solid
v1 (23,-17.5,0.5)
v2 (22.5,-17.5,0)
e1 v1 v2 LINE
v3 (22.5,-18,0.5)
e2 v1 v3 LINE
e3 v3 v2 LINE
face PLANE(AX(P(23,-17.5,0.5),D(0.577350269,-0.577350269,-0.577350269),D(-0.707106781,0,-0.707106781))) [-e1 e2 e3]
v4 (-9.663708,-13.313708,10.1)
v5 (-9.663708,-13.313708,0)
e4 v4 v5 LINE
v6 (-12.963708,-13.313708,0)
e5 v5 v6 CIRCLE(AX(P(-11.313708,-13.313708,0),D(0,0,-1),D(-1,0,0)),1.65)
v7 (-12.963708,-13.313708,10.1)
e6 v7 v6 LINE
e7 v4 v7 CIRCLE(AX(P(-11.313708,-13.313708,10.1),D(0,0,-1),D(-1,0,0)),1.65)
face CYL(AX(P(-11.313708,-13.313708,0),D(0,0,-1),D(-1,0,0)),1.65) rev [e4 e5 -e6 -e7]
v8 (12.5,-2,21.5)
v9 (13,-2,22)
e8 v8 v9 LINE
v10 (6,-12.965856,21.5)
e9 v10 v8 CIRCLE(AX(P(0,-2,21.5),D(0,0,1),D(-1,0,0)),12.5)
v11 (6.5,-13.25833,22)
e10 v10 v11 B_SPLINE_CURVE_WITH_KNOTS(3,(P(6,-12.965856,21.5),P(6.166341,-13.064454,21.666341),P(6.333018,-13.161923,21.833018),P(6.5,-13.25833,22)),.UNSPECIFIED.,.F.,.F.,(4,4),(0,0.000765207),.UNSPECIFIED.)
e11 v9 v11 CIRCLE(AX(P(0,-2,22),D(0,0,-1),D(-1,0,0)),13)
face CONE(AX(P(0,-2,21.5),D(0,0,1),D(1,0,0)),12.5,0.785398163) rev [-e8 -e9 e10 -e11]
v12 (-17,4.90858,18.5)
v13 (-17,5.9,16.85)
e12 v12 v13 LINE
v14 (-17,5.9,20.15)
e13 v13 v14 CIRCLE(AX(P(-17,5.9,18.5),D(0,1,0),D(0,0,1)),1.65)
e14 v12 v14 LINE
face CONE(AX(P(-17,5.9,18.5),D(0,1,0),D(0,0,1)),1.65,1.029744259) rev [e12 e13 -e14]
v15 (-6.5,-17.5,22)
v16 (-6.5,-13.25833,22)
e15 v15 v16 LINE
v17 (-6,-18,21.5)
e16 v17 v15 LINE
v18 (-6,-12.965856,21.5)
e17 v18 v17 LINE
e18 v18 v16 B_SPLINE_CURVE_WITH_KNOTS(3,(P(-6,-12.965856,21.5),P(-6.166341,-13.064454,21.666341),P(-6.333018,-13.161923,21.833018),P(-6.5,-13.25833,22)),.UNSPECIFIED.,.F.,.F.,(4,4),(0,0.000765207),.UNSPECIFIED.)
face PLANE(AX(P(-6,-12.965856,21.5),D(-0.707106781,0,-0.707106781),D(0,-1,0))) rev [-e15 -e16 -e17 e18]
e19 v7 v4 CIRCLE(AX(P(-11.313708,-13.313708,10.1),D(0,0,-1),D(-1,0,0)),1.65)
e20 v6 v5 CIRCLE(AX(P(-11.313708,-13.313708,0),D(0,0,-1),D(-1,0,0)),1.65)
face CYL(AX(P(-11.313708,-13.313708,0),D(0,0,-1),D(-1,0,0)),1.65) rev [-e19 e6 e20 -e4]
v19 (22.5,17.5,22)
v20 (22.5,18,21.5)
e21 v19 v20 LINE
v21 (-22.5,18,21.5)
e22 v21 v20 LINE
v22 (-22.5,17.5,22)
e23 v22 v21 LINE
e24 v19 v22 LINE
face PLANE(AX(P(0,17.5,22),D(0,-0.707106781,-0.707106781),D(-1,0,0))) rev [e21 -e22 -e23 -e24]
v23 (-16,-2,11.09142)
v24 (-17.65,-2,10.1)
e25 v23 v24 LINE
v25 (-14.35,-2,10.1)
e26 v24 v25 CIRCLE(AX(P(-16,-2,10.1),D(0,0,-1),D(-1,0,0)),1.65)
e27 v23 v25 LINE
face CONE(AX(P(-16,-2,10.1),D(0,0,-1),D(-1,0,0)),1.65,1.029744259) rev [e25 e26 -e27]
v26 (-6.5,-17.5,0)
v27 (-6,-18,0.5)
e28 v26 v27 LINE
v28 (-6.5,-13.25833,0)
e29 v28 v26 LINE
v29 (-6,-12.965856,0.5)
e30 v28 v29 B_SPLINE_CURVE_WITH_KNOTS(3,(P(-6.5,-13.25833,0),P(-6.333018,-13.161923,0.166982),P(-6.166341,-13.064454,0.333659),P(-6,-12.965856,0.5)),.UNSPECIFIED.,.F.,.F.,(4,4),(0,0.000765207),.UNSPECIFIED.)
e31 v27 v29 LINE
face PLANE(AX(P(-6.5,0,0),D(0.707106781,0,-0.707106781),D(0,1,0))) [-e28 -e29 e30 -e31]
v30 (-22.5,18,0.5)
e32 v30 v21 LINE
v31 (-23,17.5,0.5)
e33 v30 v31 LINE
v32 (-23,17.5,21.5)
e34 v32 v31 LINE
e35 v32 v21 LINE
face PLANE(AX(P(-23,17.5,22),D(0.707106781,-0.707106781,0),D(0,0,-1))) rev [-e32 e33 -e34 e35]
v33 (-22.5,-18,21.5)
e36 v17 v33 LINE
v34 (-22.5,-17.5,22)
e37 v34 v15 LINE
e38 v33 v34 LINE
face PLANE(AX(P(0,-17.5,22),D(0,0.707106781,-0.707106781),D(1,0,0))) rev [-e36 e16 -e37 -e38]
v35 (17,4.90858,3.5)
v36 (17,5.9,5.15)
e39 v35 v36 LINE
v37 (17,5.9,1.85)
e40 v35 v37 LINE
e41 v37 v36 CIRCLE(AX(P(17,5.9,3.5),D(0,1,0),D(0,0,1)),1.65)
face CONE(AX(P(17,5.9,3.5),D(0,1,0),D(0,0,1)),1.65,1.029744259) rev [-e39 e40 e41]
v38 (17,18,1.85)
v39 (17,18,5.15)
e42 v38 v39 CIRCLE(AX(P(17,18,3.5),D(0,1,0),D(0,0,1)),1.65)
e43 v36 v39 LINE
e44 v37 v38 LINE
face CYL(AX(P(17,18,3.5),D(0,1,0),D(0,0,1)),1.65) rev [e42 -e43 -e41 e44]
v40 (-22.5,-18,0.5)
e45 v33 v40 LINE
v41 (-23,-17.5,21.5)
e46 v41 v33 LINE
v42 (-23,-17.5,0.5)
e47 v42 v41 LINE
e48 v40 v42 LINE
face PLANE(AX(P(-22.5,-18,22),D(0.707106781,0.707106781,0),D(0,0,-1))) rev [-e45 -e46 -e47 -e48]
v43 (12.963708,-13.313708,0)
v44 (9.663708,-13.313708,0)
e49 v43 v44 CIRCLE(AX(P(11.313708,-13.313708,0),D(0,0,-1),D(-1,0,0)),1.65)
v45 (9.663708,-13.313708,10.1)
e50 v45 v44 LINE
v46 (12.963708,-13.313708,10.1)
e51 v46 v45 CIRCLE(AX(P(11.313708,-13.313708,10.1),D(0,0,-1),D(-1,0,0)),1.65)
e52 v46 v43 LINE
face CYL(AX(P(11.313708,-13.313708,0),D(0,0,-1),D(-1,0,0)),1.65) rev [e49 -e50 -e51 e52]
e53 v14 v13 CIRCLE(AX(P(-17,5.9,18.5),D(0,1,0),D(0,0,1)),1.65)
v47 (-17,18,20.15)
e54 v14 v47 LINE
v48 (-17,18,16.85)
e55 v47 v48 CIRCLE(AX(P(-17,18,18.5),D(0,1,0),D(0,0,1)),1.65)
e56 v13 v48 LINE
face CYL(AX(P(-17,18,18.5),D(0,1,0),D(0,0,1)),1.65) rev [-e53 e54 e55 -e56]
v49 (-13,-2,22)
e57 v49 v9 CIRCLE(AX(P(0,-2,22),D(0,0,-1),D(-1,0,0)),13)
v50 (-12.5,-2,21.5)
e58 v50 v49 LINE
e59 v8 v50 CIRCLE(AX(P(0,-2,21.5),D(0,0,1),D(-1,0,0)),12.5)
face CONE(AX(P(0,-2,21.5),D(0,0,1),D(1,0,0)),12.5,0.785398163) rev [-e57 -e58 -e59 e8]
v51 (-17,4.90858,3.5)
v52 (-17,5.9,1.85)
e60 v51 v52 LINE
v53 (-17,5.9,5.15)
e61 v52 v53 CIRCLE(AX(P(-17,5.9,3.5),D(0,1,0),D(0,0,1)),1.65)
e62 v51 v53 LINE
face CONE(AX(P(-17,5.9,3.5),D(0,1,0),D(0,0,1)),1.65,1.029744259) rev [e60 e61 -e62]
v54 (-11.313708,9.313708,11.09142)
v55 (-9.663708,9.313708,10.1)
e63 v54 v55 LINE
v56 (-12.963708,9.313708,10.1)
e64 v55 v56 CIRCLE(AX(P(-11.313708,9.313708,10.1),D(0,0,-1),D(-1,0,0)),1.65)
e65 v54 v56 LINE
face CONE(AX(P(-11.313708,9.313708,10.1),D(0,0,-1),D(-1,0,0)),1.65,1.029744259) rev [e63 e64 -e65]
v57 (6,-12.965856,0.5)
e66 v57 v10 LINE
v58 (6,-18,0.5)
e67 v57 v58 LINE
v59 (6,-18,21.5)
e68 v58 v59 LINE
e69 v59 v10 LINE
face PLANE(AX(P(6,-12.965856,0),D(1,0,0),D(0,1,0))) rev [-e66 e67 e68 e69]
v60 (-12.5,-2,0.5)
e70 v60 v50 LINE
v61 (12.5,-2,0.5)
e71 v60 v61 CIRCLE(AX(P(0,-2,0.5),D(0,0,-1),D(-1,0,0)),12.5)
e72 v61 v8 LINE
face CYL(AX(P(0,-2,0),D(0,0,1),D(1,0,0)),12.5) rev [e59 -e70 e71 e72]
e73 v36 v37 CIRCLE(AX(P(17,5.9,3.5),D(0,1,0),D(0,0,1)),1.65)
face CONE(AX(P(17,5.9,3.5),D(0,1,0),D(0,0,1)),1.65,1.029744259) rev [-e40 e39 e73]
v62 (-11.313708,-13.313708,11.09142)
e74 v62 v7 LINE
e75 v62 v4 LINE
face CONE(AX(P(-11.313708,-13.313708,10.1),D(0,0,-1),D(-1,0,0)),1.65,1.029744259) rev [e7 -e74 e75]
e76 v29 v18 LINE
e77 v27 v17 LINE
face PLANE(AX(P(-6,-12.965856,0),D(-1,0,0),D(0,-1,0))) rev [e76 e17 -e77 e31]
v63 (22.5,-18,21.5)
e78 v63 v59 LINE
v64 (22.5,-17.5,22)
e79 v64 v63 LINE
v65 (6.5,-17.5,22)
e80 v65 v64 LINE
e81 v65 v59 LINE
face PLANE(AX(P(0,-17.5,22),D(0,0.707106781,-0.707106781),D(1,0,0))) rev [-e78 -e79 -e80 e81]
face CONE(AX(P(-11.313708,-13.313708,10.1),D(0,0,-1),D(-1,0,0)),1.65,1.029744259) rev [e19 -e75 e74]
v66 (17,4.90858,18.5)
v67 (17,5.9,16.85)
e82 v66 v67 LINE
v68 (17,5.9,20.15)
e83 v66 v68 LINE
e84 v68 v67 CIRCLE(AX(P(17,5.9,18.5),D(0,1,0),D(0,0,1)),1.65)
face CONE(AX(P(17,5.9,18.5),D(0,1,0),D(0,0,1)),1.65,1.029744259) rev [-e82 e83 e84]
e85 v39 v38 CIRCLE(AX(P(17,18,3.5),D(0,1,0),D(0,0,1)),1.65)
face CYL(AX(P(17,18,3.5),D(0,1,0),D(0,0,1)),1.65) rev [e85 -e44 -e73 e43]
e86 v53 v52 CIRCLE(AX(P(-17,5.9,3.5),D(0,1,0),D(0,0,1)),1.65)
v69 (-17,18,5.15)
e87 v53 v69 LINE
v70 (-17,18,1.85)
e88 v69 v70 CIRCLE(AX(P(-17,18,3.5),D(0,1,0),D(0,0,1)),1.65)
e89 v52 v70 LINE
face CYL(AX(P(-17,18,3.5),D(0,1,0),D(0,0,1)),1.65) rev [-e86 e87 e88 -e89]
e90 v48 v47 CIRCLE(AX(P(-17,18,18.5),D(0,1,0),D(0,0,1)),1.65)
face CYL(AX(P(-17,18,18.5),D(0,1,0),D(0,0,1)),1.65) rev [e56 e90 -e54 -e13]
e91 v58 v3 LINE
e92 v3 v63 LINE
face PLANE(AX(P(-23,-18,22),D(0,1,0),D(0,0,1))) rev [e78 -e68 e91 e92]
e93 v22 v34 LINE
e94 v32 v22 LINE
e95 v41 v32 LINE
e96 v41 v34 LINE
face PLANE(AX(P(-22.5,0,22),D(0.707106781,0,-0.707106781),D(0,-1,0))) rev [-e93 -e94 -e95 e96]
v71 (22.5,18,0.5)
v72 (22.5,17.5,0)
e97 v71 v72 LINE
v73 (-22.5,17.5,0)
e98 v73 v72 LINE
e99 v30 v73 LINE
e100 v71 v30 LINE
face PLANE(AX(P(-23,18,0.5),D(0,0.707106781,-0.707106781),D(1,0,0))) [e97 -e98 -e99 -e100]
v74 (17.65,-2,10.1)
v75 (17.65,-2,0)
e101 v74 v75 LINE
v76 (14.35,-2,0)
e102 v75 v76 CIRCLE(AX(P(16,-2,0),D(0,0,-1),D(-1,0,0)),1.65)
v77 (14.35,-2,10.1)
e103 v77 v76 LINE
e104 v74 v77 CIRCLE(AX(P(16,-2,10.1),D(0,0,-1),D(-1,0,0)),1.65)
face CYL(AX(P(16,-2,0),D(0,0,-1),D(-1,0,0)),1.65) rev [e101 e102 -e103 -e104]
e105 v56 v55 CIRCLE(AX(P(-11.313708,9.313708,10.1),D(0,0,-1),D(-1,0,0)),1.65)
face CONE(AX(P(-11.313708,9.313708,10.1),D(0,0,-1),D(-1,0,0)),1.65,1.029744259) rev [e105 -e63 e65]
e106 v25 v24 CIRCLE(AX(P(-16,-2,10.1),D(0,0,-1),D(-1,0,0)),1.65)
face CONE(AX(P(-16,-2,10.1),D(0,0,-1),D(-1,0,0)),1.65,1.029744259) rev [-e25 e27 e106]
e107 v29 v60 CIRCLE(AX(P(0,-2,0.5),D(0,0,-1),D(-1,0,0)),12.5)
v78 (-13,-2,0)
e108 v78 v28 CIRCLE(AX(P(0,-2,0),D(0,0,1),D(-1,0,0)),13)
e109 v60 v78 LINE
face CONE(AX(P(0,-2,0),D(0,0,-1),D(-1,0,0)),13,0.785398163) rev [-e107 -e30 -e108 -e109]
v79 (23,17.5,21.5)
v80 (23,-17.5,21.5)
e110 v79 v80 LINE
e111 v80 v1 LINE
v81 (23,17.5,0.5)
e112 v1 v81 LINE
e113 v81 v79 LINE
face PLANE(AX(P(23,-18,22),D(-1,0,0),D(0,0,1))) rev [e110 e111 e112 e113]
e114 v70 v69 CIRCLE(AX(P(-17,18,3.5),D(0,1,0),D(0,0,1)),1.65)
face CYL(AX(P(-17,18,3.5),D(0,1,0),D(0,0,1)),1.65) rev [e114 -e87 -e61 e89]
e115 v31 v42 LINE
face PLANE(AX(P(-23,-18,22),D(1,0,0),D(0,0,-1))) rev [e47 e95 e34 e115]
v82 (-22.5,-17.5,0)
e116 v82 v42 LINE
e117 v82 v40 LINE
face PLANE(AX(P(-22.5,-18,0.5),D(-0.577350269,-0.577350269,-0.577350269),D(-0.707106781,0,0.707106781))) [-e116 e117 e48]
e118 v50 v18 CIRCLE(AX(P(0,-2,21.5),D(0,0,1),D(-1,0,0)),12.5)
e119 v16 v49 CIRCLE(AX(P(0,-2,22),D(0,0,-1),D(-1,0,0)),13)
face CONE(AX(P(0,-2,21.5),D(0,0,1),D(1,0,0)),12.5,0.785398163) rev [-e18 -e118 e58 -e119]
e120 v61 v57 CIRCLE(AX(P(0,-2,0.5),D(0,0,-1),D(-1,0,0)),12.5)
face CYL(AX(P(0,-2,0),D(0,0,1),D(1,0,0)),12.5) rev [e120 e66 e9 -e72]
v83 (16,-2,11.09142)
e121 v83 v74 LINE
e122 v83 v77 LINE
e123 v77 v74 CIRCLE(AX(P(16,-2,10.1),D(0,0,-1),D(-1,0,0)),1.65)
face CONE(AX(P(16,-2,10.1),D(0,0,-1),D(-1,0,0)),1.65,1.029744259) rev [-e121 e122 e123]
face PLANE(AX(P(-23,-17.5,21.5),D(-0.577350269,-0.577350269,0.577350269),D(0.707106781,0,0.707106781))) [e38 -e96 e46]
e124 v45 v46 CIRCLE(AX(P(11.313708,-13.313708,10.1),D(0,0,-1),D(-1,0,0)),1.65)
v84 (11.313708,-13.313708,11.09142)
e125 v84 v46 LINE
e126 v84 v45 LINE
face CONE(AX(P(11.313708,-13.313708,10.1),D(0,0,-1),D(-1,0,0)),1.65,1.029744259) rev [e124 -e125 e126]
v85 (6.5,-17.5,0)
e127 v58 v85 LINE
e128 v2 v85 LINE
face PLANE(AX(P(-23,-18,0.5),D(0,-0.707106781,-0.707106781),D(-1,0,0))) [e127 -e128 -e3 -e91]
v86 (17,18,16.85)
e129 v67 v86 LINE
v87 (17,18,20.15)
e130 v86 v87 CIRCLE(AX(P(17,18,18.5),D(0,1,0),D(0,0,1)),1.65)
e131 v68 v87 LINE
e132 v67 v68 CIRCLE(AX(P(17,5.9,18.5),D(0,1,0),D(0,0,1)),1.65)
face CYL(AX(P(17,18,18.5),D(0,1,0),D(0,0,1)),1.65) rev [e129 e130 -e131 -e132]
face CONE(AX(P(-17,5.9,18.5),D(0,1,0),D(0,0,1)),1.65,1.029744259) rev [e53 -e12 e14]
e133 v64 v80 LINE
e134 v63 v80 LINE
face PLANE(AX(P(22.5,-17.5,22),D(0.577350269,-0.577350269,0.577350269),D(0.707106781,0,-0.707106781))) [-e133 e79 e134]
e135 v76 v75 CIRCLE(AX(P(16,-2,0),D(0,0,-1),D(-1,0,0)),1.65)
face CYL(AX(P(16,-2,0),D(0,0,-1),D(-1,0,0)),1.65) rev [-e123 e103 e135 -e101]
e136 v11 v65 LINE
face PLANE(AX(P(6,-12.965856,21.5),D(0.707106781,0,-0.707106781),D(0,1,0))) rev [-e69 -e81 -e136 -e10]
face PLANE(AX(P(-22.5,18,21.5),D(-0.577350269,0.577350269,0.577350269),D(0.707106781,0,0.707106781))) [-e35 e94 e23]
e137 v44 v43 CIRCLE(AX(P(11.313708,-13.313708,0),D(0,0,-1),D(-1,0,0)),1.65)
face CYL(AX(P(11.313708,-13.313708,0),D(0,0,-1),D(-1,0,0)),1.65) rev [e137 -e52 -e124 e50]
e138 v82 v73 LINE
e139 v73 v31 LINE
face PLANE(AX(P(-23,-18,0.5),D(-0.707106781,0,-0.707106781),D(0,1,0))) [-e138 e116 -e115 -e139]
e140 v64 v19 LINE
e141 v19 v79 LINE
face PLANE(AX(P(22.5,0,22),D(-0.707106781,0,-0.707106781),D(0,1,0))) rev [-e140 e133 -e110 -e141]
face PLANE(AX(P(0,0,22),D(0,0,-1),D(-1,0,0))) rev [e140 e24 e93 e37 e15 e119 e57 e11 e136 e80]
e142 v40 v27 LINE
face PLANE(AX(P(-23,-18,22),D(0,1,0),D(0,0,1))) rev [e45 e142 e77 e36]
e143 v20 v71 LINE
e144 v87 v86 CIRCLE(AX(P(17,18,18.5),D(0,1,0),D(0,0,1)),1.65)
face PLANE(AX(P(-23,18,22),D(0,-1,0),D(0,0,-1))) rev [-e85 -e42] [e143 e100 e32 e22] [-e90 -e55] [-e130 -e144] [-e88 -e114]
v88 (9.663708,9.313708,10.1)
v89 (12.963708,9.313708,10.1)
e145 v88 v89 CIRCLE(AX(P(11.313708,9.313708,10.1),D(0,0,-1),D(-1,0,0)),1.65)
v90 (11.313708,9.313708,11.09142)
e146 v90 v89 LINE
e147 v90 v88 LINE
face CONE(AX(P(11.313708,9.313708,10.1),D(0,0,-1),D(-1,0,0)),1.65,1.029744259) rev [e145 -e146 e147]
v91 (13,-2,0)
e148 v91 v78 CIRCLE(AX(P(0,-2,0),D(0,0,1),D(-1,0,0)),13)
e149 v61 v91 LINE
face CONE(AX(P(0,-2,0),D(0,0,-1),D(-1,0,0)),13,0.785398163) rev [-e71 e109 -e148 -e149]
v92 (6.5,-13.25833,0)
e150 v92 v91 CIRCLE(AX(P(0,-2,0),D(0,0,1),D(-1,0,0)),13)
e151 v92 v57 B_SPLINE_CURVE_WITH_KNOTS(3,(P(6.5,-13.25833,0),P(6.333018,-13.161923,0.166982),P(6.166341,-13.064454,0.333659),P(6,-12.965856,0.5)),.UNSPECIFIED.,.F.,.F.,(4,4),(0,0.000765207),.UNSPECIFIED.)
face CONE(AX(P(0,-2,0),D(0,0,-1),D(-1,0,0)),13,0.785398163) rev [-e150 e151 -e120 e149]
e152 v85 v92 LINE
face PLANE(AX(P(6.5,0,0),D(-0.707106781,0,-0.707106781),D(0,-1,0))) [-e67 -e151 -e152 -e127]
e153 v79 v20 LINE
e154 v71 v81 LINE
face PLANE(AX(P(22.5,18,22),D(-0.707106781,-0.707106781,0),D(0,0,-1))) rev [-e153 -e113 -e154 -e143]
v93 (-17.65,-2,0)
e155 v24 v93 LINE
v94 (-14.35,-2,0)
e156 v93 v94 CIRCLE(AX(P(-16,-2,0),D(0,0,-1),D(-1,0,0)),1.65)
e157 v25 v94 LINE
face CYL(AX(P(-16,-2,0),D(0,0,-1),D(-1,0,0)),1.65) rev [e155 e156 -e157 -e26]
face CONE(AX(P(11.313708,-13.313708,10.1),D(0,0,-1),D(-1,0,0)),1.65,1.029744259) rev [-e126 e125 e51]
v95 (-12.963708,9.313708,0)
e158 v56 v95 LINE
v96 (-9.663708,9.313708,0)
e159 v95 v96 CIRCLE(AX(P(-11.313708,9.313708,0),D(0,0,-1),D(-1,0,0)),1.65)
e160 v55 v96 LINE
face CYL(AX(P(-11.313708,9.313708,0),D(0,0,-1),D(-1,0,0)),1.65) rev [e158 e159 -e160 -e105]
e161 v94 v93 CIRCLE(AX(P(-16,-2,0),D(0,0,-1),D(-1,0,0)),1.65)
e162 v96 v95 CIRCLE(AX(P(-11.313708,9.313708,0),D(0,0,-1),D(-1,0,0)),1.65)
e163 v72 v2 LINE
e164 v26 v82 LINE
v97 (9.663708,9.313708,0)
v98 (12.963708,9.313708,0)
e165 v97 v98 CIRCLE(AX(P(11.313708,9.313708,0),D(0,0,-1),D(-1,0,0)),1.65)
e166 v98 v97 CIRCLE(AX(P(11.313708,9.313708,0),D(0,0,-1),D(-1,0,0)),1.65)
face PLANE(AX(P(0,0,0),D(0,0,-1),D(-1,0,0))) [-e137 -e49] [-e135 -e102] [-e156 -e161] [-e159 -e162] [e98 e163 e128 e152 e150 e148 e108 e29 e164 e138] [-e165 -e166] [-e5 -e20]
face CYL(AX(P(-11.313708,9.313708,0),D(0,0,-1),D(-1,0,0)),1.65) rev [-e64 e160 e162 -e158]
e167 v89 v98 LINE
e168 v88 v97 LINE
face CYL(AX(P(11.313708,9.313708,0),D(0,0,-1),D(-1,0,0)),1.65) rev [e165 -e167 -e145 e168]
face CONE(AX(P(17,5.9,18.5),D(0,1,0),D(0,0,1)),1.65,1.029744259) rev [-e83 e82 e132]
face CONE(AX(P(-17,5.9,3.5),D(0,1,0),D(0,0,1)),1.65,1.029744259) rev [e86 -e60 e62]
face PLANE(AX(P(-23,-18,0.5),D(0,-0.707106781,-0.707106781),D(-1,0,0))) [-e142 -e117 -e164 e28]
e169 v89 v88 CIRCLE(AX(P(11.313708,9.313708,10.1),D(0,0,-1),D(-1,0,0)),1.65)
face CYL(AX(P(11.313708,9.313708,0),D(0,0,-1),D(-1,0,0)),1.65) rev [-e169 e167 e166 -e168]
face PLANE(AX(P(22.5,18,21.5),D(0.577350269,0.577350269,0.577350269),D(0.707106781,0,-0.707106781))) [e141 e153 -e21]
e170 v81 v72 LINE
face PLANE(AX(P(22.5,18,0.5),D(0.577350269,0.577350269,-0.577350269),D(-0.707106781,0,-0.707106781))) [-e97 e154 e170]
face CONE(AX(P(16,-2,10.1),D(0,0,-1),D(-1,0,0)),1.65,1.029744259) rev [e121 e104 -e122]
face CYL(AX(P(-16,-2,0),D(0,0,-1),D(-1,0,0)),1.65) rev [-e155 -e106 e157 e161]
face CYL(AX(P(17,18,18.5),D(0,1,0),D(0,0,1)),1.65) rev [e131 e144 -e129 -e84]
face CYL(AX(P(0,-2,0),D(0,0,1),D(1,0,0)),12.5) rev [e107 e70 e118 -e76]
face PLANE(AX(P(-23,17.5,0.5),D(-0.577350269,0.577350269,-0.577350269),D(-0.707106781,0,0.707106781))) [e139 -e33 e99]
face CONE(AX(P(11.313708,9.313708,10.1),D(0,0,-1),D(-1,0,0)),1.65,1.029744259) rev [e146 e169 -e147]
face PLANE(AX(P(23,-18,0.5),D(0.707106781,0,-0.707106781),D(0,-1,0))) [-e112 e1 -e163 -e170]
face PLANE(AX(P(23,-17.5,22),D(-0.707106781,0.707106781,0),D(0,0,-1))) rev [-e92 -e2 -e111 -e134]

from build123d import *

# Parameters (mm, degrees)
SKETCH_1_W             = 46
SKETCH_1_H             = 36
EXTRUDE_1_DEPTH        = 22
CUT_EXTRUDE_2_DEPTH    = 37.565010598
CHAMFER_1_SIZE         = 0.5
HOLE_WIZARD_M4_1_D     = 3.3
HOLE_WIZARD_M4_1_DEPTH = 12.1
HOLE_WIZARD_M4_1_TIP   = 0.991420021
HOLE_WIZARD_M4_2_D     = 3.3
HOLE_WIZARD_M4_2_DEPTH = 10.1
HOLE_WIZARD_M4_2_TIP   = 0.991420021


with BuildPart() as part:
    # 草图1 → 凸台-拉伸1 (new body)
    with BuildSketch(Plane.XY):
        Rectangle(SKETCH_1_W, SKETCH_1_H)
    extrude(amount=EXTRUDE_1_DEPTH)

    # 草图5 → 切除-拉伸2 (cut, through all)
    with BuildSketch(Plane.XY.offset(22)):
        with BuildLine():
            Line((-6, -12.9658561), (-6, -18))
            Line((-6, -18), (6, -18))
            Line((6, -18), (6, -12.9658561))
            ThreePointArc((6, -12.9658561), (0, 10.5), (-6, -12.9658561))
        make_face()
    extrude(amount=-CUT_EXTRUDE_2_DEPTH, mode=Mode.SUBTRACT)

    # 倒角1
    chamfer_1_edges = [part.edges().sort_by_distance(p)[0] for p in [
        (-23, 0, 22),
        (-14.5, -18, 22),
        (14.5, -18, 0),
        (14.5, -18, 22),
        (0, 10.5, 0),
        (6, -15.48292805, 0),
        (-6, -15.48292805, 0),
        (0, 10.5, 22),
        (-6, -15.48292805, 22),
        (6, -15.48292805, 22),
        (23, 0, 22),
        (-14.5, -18, 0),
        (-23, 0, 0),
        (0, 18, 0),
        (23, 0, 0),
        (0, 18, 22),
        (23, -18, 11),
        (-23, -18, 11),
        (-23, 18, 11),
        (23, 18, 11),
    ]]
    chamfer(chamfer_1_edges, length=CHAMFER_1_SIZE)

    # M4 螺纹孔1
    with Locations(Plane(origin=(0, 18, 0), x_dir=(1, 0, 0), z_dir=(0, 1, 0))):
        with Locations((17, -18.5), (17, -3.5), (-17, -3.5), (-17, -18.5)):
            Hole(HOLE_WIZARD_M4_1_D / 2, depth=HOLE_WIZARD_M4_1_DEPTH)
            with Locations((0, 0, -(HOLE_WIZARD_M4_1_DEPTH + HOLE_WIZARD_M4_1_TIP / 2))):  # 118° drill point
                Cone(0, HOLE_WIZARD_M4_1_D / 2, HOLE_WIZARD_M4_1_TIP, mode=Mode.SUBTRACT)

    # M4 螺纹孔2
    with Locations(Plane(origin=(0, 0, 0), x_dir=(-1, 0, 0), z_dir=(0, 0, -1))):
        with Locations((-16, -2), (-11.313708499, 9.313708499), (11.313708499, 9.313708499), (16, -2), (-11.313708499, -13.313708499), (11.313708499, -13.313708499)):
            Hole(HOLE_WIZARD_M4_2_D / 2, depth=HOLE_WIZARD_M4_2_DEPTH)
            with Locations((0, 0, -(HOLE_WIZARD_M4_2_DEPTH + HOLE_WIZARD_M4_2_TIP / 2))):  # 118° drill point
                Cone(0, HOLE_WIZARD_M4_2_D / 2, HOLE_WIZARD_M4_2_TIP, mode=Mode.SUBTRACT)


solid = part.part
